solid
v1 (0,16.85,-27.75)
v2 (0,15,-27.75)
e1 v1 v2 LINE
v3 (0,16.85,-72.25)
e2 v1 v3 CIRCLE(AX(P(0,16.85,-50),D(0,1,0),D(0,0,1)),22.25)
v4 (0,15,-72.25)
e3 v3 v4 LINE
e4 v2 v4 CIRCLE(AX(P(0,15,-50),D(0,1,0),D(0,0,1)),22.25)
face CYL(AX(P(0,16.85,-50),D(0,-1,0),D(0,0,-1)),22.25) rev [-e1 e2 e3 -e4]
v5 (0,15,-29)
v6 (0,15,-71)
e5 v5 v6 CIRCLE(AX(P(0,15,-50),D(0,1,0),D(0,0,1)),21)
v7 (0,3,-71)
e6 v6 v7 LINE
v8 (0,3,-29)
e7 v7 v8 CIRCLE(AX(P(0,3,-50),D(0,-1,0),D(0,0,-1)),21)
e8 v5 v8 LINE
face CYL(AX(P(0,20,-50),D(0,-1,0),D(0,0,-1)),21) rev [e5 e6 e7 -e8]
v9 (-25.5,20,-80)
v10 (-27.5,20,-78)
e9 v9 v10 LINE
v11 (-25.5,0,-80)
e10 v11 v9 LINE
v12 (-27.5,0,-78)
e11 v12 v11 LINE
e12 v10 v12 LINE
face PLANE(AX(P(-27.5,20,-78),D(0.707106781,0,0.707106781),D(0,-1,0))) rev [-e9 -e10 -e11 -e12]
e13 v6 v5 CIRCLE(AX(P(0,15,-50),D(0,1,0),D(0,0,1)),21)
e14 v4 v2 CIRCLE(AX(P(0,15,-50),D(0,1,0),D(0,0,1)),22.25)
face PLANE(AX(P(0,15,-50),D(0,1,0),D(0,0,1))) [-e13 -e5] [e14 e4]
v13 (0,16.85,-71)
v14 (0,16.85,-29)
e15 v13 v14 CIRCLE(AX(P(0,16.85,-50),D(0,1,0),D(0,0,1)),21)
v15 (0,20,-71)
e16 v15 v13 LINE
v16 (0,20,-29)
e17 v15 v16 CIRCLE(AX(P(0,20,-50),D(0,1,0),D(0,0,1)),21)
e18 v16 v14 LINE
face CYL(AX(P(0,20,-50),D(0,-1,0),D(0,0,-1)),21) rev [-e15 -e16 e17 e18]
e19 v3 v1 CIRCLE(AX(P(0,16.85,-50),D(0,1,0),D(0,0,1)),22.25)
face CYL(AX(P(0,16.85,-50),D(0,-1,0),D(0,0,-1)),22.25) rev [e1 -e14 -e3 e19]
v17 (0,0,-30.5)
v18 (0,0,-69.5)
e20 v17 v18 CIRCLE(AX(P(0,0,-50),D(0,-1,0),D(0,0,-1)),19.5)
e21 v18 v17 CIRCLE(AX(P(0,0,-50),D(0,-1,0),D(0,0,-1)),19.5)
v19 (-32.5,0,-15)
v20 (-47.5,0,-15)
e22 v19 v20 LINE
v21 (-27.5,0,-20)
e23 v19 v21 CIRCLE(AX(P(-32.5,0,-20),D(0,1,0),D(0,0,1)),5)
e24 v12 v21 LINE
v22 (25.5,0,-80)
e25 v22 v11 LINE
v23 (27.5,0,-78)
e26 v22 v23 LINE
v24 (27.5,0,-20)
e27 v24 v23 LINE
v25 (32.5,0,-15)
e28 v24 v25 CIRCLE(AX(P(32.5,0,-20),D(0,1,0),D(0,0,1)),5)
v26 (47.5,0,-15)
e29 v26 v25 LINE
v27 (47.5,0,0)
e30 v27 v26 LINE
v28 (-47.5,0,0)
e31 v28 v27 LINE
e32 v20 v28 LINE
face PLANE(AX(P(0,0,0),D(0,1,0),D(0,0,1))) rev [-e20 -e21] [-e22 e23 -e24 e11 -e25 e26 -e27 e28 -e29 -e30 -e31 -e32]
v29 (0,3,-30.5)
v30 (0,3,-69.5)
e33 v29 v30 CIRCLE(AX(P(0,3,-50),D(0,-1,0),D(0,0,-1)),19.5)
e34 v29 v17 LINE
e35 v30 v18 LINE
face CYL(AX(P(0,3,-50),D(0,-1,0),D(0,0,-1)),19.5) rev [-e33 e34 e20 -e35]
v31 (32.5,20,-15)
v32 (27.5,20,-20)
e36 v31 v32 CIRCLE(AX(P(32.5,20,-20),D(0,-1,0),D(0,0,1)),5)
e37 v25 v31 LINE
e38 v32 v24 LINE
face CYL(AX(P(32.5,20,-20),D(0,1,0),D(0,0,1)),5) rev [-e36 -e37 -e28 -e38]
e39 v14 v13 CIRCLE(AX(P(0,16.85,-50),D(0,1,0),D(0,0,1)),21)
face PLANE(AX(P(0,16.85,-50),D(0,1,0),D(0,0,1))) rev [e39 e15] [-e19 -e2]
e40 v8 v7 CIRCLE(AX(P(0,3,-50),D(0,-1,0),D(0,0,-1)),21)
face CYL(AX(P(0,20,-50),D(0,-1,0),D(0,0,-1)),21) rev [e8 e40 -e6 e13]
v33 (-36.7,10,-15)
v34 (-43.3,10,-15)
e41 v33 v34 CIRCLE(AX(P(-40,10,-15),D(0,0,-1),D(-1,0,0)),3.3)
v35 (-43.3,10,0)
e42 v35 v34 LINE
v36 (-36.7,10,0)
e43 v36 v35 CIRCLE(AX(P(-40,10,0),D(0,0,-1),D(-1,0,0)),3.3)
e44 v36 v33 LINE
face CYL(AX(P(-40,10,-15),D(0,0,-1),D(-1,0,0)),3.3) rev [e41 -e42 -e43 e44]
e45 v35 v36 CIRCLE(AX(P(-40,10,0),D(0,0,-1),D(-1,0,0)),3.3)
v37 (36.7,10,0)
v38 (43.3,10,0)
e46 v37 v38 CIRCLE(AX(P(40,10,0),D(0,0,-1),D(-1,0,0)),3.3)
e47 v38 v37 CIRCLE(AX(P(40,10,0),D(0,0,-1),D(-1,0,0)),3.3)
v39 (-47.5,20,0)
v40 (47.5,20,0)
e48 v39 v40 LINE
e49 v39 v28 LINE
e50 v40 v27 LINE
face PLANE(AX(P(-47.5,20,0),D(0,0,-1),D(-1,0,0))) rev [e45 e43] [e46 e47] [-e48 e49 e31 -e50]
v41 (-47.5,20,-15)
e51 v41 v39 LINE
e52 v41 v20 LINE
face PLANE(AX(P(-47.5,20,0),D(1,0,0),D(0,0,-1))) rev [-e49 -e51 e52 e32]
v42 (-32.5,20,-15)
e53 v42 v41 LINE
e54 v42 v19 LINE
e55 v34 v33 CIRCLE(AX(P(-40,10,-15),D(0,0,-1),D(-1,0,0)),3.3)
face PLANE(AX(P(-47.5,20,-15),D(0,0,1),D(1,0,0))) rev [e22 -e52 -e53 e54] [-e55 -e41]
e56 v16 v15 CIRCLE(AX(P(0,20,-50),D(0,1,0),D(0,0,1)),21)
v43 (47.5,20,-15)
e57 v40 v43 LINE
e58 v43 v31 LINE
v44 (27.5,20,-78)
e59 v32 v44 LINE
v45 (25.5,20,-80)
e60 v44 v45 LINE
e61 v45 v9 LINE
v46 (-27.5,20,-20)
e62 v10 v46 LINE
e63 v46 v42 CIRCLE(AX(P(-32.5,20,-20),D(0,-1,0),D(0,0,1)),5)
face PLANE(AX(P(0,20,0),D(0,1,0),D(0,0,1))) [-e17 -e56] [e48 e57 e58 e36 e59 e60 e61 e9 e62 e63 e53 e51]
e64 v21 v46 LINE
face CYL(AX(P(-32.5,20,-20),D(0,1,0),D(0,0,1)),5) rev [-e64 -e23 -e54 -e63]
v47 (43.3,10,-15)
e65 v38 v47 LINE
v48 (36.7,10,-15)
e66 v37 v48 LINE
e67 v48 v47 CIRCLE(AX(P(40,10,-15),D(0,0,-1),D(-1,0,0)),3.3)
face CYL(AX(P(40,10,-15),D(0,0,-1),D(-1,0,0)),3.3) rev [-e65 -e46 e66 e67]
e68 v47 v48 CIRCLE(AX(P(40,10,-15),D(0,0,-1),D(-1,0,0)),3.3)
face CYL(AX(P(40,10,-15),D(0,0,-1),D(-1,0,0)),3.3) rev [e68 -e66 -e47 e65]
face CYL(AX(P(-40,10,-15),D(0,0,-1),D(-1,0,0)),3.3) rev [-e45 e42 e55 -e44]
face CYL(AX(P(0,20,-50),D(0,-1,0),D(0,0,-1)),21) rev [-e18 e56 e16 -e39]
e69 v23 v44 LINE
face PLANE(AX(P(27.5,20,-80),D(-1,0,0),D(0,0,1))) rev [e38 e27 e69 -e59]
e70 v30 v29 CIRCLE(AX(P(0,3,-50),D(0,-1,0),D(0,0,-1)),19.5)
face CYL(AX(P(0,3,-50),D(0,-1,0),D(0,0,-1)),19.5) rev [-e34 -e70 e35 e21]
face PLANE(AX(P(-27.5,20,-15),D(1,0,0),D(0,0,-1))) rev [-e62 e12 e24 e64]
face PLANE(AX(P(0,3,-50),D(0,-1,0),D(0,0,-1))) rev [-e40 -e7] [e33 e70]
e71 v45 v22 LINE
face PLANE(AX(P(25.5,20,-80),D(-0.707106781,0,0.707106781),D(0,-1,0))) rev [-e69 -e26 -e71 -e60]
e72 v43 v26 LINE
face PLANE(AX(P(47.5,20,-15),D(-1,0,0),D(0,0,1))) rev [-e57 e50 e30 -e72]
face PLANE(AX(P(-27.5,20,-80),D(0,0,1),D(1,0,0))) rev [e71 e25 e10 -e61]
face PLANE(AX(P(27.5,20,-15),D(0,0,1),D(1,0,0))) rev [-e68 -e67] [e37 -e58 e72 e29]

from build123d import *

# Parameters (mm, degrees)
SKETCH_1_R          = 21
EXTRUDE_1_DEPTH     = 20
CHAMFER_1_SIZE      = 2
FILLET_1_R          = 5
SKETCH_2_R          = 21
SKETCH_2_R_2        = 19.5
EXTRUDE_2_DEPTH     = 3
HOLE_WIZARD_M6_1_D  = 6.6
SKETCH_9_R          = 22.25
SKETCH_9_R_2        = 21
CUT_EXTRUDE_1_DEPTH = 1.85


with BuildPart() as part:
    # 草图1 → 凸台-拉伸1 (new body)
    with BuildSketch(Plane(origin=(0, 0, 0), x_dir=(1, 0, 0), z_dir=(0, 1, 0))):
        Polygon((-47.5, 0), (47.5, 0), (47.5, 15), (27.5, 15), (27.5, 80), (-27.5, 80), (-27.5, 15), (-47.5, 15), align=None)
        with Locations(Location((0, 50, 0), (0, 0, 270))):
            Circle(SKETCH_1_R, mode=Mode.SUBTRACT)
    extrude(amount=EXTRUDE_1_DEPTH)

    # 倒角1
    chamfer_1_edges = [part.edges().sort_by_distance(p)[0] for p in [
        (-27.5, 10, -80),
        (27.5, 10, -80),
    ]]
    chamfer(chamfer_1_edges, length=CHAMFER_1_SIZE)

    # 圆角1
    fillet_1_edges = [part.edges().sort_by_distance(p)[0] for p in [
        (-27.5, 10, -15),
        (27.5, 10, -15),
    ]]
    fillet(fillet_1_edges, radius=FILLET_1_R)

    # 草图2 → 凸台-拉伸2 (add)
    with BuildSketch(Plane.XZ):
        with Locations(Location((0, -50, 0), (0, 0, 270))):
            Circle(SKETCH_2_R)
        with Locations(Location((0, -50, 0), (0, 0, 270))):
            Circle(SKETCH_2_R_2, mode=Mode.SUBTRACT)
    extrude(amount=-EXTRUDE_2_DEPTH)

    # M6 间隙孔1 (through all)
    with Locations(Plane(origin=(0, 0, -15), x_dir=(-1, 0, 0), z_dir=(0, 0, -1))):
        with Locations((-40, 10), (40, 10)):
            Hole(HOLE_WIZARD_M6_1_D / 2)

    # 草图9 → 切除-拉伸1 (cut)
    with BuildSketch(Plane(origin=(0, 15, 0), x_dir=(1, 0, 0), z_dir=(0, 1, 0))):
        with Locations(Location((0, 50, 0), (0, 0, 270))):
            Circle(SKETCH_9_R)
        with Locations(Location((0, 50, 0), (0, 0, 90))):
            Circle(SKETCH_9_R_2, mode=Mode.SUBTRACT)
    extrude(amount=CUT_EXTRUDE_1_DEPTH, mode=Mode.SUBTRACT)


solid = part.part
